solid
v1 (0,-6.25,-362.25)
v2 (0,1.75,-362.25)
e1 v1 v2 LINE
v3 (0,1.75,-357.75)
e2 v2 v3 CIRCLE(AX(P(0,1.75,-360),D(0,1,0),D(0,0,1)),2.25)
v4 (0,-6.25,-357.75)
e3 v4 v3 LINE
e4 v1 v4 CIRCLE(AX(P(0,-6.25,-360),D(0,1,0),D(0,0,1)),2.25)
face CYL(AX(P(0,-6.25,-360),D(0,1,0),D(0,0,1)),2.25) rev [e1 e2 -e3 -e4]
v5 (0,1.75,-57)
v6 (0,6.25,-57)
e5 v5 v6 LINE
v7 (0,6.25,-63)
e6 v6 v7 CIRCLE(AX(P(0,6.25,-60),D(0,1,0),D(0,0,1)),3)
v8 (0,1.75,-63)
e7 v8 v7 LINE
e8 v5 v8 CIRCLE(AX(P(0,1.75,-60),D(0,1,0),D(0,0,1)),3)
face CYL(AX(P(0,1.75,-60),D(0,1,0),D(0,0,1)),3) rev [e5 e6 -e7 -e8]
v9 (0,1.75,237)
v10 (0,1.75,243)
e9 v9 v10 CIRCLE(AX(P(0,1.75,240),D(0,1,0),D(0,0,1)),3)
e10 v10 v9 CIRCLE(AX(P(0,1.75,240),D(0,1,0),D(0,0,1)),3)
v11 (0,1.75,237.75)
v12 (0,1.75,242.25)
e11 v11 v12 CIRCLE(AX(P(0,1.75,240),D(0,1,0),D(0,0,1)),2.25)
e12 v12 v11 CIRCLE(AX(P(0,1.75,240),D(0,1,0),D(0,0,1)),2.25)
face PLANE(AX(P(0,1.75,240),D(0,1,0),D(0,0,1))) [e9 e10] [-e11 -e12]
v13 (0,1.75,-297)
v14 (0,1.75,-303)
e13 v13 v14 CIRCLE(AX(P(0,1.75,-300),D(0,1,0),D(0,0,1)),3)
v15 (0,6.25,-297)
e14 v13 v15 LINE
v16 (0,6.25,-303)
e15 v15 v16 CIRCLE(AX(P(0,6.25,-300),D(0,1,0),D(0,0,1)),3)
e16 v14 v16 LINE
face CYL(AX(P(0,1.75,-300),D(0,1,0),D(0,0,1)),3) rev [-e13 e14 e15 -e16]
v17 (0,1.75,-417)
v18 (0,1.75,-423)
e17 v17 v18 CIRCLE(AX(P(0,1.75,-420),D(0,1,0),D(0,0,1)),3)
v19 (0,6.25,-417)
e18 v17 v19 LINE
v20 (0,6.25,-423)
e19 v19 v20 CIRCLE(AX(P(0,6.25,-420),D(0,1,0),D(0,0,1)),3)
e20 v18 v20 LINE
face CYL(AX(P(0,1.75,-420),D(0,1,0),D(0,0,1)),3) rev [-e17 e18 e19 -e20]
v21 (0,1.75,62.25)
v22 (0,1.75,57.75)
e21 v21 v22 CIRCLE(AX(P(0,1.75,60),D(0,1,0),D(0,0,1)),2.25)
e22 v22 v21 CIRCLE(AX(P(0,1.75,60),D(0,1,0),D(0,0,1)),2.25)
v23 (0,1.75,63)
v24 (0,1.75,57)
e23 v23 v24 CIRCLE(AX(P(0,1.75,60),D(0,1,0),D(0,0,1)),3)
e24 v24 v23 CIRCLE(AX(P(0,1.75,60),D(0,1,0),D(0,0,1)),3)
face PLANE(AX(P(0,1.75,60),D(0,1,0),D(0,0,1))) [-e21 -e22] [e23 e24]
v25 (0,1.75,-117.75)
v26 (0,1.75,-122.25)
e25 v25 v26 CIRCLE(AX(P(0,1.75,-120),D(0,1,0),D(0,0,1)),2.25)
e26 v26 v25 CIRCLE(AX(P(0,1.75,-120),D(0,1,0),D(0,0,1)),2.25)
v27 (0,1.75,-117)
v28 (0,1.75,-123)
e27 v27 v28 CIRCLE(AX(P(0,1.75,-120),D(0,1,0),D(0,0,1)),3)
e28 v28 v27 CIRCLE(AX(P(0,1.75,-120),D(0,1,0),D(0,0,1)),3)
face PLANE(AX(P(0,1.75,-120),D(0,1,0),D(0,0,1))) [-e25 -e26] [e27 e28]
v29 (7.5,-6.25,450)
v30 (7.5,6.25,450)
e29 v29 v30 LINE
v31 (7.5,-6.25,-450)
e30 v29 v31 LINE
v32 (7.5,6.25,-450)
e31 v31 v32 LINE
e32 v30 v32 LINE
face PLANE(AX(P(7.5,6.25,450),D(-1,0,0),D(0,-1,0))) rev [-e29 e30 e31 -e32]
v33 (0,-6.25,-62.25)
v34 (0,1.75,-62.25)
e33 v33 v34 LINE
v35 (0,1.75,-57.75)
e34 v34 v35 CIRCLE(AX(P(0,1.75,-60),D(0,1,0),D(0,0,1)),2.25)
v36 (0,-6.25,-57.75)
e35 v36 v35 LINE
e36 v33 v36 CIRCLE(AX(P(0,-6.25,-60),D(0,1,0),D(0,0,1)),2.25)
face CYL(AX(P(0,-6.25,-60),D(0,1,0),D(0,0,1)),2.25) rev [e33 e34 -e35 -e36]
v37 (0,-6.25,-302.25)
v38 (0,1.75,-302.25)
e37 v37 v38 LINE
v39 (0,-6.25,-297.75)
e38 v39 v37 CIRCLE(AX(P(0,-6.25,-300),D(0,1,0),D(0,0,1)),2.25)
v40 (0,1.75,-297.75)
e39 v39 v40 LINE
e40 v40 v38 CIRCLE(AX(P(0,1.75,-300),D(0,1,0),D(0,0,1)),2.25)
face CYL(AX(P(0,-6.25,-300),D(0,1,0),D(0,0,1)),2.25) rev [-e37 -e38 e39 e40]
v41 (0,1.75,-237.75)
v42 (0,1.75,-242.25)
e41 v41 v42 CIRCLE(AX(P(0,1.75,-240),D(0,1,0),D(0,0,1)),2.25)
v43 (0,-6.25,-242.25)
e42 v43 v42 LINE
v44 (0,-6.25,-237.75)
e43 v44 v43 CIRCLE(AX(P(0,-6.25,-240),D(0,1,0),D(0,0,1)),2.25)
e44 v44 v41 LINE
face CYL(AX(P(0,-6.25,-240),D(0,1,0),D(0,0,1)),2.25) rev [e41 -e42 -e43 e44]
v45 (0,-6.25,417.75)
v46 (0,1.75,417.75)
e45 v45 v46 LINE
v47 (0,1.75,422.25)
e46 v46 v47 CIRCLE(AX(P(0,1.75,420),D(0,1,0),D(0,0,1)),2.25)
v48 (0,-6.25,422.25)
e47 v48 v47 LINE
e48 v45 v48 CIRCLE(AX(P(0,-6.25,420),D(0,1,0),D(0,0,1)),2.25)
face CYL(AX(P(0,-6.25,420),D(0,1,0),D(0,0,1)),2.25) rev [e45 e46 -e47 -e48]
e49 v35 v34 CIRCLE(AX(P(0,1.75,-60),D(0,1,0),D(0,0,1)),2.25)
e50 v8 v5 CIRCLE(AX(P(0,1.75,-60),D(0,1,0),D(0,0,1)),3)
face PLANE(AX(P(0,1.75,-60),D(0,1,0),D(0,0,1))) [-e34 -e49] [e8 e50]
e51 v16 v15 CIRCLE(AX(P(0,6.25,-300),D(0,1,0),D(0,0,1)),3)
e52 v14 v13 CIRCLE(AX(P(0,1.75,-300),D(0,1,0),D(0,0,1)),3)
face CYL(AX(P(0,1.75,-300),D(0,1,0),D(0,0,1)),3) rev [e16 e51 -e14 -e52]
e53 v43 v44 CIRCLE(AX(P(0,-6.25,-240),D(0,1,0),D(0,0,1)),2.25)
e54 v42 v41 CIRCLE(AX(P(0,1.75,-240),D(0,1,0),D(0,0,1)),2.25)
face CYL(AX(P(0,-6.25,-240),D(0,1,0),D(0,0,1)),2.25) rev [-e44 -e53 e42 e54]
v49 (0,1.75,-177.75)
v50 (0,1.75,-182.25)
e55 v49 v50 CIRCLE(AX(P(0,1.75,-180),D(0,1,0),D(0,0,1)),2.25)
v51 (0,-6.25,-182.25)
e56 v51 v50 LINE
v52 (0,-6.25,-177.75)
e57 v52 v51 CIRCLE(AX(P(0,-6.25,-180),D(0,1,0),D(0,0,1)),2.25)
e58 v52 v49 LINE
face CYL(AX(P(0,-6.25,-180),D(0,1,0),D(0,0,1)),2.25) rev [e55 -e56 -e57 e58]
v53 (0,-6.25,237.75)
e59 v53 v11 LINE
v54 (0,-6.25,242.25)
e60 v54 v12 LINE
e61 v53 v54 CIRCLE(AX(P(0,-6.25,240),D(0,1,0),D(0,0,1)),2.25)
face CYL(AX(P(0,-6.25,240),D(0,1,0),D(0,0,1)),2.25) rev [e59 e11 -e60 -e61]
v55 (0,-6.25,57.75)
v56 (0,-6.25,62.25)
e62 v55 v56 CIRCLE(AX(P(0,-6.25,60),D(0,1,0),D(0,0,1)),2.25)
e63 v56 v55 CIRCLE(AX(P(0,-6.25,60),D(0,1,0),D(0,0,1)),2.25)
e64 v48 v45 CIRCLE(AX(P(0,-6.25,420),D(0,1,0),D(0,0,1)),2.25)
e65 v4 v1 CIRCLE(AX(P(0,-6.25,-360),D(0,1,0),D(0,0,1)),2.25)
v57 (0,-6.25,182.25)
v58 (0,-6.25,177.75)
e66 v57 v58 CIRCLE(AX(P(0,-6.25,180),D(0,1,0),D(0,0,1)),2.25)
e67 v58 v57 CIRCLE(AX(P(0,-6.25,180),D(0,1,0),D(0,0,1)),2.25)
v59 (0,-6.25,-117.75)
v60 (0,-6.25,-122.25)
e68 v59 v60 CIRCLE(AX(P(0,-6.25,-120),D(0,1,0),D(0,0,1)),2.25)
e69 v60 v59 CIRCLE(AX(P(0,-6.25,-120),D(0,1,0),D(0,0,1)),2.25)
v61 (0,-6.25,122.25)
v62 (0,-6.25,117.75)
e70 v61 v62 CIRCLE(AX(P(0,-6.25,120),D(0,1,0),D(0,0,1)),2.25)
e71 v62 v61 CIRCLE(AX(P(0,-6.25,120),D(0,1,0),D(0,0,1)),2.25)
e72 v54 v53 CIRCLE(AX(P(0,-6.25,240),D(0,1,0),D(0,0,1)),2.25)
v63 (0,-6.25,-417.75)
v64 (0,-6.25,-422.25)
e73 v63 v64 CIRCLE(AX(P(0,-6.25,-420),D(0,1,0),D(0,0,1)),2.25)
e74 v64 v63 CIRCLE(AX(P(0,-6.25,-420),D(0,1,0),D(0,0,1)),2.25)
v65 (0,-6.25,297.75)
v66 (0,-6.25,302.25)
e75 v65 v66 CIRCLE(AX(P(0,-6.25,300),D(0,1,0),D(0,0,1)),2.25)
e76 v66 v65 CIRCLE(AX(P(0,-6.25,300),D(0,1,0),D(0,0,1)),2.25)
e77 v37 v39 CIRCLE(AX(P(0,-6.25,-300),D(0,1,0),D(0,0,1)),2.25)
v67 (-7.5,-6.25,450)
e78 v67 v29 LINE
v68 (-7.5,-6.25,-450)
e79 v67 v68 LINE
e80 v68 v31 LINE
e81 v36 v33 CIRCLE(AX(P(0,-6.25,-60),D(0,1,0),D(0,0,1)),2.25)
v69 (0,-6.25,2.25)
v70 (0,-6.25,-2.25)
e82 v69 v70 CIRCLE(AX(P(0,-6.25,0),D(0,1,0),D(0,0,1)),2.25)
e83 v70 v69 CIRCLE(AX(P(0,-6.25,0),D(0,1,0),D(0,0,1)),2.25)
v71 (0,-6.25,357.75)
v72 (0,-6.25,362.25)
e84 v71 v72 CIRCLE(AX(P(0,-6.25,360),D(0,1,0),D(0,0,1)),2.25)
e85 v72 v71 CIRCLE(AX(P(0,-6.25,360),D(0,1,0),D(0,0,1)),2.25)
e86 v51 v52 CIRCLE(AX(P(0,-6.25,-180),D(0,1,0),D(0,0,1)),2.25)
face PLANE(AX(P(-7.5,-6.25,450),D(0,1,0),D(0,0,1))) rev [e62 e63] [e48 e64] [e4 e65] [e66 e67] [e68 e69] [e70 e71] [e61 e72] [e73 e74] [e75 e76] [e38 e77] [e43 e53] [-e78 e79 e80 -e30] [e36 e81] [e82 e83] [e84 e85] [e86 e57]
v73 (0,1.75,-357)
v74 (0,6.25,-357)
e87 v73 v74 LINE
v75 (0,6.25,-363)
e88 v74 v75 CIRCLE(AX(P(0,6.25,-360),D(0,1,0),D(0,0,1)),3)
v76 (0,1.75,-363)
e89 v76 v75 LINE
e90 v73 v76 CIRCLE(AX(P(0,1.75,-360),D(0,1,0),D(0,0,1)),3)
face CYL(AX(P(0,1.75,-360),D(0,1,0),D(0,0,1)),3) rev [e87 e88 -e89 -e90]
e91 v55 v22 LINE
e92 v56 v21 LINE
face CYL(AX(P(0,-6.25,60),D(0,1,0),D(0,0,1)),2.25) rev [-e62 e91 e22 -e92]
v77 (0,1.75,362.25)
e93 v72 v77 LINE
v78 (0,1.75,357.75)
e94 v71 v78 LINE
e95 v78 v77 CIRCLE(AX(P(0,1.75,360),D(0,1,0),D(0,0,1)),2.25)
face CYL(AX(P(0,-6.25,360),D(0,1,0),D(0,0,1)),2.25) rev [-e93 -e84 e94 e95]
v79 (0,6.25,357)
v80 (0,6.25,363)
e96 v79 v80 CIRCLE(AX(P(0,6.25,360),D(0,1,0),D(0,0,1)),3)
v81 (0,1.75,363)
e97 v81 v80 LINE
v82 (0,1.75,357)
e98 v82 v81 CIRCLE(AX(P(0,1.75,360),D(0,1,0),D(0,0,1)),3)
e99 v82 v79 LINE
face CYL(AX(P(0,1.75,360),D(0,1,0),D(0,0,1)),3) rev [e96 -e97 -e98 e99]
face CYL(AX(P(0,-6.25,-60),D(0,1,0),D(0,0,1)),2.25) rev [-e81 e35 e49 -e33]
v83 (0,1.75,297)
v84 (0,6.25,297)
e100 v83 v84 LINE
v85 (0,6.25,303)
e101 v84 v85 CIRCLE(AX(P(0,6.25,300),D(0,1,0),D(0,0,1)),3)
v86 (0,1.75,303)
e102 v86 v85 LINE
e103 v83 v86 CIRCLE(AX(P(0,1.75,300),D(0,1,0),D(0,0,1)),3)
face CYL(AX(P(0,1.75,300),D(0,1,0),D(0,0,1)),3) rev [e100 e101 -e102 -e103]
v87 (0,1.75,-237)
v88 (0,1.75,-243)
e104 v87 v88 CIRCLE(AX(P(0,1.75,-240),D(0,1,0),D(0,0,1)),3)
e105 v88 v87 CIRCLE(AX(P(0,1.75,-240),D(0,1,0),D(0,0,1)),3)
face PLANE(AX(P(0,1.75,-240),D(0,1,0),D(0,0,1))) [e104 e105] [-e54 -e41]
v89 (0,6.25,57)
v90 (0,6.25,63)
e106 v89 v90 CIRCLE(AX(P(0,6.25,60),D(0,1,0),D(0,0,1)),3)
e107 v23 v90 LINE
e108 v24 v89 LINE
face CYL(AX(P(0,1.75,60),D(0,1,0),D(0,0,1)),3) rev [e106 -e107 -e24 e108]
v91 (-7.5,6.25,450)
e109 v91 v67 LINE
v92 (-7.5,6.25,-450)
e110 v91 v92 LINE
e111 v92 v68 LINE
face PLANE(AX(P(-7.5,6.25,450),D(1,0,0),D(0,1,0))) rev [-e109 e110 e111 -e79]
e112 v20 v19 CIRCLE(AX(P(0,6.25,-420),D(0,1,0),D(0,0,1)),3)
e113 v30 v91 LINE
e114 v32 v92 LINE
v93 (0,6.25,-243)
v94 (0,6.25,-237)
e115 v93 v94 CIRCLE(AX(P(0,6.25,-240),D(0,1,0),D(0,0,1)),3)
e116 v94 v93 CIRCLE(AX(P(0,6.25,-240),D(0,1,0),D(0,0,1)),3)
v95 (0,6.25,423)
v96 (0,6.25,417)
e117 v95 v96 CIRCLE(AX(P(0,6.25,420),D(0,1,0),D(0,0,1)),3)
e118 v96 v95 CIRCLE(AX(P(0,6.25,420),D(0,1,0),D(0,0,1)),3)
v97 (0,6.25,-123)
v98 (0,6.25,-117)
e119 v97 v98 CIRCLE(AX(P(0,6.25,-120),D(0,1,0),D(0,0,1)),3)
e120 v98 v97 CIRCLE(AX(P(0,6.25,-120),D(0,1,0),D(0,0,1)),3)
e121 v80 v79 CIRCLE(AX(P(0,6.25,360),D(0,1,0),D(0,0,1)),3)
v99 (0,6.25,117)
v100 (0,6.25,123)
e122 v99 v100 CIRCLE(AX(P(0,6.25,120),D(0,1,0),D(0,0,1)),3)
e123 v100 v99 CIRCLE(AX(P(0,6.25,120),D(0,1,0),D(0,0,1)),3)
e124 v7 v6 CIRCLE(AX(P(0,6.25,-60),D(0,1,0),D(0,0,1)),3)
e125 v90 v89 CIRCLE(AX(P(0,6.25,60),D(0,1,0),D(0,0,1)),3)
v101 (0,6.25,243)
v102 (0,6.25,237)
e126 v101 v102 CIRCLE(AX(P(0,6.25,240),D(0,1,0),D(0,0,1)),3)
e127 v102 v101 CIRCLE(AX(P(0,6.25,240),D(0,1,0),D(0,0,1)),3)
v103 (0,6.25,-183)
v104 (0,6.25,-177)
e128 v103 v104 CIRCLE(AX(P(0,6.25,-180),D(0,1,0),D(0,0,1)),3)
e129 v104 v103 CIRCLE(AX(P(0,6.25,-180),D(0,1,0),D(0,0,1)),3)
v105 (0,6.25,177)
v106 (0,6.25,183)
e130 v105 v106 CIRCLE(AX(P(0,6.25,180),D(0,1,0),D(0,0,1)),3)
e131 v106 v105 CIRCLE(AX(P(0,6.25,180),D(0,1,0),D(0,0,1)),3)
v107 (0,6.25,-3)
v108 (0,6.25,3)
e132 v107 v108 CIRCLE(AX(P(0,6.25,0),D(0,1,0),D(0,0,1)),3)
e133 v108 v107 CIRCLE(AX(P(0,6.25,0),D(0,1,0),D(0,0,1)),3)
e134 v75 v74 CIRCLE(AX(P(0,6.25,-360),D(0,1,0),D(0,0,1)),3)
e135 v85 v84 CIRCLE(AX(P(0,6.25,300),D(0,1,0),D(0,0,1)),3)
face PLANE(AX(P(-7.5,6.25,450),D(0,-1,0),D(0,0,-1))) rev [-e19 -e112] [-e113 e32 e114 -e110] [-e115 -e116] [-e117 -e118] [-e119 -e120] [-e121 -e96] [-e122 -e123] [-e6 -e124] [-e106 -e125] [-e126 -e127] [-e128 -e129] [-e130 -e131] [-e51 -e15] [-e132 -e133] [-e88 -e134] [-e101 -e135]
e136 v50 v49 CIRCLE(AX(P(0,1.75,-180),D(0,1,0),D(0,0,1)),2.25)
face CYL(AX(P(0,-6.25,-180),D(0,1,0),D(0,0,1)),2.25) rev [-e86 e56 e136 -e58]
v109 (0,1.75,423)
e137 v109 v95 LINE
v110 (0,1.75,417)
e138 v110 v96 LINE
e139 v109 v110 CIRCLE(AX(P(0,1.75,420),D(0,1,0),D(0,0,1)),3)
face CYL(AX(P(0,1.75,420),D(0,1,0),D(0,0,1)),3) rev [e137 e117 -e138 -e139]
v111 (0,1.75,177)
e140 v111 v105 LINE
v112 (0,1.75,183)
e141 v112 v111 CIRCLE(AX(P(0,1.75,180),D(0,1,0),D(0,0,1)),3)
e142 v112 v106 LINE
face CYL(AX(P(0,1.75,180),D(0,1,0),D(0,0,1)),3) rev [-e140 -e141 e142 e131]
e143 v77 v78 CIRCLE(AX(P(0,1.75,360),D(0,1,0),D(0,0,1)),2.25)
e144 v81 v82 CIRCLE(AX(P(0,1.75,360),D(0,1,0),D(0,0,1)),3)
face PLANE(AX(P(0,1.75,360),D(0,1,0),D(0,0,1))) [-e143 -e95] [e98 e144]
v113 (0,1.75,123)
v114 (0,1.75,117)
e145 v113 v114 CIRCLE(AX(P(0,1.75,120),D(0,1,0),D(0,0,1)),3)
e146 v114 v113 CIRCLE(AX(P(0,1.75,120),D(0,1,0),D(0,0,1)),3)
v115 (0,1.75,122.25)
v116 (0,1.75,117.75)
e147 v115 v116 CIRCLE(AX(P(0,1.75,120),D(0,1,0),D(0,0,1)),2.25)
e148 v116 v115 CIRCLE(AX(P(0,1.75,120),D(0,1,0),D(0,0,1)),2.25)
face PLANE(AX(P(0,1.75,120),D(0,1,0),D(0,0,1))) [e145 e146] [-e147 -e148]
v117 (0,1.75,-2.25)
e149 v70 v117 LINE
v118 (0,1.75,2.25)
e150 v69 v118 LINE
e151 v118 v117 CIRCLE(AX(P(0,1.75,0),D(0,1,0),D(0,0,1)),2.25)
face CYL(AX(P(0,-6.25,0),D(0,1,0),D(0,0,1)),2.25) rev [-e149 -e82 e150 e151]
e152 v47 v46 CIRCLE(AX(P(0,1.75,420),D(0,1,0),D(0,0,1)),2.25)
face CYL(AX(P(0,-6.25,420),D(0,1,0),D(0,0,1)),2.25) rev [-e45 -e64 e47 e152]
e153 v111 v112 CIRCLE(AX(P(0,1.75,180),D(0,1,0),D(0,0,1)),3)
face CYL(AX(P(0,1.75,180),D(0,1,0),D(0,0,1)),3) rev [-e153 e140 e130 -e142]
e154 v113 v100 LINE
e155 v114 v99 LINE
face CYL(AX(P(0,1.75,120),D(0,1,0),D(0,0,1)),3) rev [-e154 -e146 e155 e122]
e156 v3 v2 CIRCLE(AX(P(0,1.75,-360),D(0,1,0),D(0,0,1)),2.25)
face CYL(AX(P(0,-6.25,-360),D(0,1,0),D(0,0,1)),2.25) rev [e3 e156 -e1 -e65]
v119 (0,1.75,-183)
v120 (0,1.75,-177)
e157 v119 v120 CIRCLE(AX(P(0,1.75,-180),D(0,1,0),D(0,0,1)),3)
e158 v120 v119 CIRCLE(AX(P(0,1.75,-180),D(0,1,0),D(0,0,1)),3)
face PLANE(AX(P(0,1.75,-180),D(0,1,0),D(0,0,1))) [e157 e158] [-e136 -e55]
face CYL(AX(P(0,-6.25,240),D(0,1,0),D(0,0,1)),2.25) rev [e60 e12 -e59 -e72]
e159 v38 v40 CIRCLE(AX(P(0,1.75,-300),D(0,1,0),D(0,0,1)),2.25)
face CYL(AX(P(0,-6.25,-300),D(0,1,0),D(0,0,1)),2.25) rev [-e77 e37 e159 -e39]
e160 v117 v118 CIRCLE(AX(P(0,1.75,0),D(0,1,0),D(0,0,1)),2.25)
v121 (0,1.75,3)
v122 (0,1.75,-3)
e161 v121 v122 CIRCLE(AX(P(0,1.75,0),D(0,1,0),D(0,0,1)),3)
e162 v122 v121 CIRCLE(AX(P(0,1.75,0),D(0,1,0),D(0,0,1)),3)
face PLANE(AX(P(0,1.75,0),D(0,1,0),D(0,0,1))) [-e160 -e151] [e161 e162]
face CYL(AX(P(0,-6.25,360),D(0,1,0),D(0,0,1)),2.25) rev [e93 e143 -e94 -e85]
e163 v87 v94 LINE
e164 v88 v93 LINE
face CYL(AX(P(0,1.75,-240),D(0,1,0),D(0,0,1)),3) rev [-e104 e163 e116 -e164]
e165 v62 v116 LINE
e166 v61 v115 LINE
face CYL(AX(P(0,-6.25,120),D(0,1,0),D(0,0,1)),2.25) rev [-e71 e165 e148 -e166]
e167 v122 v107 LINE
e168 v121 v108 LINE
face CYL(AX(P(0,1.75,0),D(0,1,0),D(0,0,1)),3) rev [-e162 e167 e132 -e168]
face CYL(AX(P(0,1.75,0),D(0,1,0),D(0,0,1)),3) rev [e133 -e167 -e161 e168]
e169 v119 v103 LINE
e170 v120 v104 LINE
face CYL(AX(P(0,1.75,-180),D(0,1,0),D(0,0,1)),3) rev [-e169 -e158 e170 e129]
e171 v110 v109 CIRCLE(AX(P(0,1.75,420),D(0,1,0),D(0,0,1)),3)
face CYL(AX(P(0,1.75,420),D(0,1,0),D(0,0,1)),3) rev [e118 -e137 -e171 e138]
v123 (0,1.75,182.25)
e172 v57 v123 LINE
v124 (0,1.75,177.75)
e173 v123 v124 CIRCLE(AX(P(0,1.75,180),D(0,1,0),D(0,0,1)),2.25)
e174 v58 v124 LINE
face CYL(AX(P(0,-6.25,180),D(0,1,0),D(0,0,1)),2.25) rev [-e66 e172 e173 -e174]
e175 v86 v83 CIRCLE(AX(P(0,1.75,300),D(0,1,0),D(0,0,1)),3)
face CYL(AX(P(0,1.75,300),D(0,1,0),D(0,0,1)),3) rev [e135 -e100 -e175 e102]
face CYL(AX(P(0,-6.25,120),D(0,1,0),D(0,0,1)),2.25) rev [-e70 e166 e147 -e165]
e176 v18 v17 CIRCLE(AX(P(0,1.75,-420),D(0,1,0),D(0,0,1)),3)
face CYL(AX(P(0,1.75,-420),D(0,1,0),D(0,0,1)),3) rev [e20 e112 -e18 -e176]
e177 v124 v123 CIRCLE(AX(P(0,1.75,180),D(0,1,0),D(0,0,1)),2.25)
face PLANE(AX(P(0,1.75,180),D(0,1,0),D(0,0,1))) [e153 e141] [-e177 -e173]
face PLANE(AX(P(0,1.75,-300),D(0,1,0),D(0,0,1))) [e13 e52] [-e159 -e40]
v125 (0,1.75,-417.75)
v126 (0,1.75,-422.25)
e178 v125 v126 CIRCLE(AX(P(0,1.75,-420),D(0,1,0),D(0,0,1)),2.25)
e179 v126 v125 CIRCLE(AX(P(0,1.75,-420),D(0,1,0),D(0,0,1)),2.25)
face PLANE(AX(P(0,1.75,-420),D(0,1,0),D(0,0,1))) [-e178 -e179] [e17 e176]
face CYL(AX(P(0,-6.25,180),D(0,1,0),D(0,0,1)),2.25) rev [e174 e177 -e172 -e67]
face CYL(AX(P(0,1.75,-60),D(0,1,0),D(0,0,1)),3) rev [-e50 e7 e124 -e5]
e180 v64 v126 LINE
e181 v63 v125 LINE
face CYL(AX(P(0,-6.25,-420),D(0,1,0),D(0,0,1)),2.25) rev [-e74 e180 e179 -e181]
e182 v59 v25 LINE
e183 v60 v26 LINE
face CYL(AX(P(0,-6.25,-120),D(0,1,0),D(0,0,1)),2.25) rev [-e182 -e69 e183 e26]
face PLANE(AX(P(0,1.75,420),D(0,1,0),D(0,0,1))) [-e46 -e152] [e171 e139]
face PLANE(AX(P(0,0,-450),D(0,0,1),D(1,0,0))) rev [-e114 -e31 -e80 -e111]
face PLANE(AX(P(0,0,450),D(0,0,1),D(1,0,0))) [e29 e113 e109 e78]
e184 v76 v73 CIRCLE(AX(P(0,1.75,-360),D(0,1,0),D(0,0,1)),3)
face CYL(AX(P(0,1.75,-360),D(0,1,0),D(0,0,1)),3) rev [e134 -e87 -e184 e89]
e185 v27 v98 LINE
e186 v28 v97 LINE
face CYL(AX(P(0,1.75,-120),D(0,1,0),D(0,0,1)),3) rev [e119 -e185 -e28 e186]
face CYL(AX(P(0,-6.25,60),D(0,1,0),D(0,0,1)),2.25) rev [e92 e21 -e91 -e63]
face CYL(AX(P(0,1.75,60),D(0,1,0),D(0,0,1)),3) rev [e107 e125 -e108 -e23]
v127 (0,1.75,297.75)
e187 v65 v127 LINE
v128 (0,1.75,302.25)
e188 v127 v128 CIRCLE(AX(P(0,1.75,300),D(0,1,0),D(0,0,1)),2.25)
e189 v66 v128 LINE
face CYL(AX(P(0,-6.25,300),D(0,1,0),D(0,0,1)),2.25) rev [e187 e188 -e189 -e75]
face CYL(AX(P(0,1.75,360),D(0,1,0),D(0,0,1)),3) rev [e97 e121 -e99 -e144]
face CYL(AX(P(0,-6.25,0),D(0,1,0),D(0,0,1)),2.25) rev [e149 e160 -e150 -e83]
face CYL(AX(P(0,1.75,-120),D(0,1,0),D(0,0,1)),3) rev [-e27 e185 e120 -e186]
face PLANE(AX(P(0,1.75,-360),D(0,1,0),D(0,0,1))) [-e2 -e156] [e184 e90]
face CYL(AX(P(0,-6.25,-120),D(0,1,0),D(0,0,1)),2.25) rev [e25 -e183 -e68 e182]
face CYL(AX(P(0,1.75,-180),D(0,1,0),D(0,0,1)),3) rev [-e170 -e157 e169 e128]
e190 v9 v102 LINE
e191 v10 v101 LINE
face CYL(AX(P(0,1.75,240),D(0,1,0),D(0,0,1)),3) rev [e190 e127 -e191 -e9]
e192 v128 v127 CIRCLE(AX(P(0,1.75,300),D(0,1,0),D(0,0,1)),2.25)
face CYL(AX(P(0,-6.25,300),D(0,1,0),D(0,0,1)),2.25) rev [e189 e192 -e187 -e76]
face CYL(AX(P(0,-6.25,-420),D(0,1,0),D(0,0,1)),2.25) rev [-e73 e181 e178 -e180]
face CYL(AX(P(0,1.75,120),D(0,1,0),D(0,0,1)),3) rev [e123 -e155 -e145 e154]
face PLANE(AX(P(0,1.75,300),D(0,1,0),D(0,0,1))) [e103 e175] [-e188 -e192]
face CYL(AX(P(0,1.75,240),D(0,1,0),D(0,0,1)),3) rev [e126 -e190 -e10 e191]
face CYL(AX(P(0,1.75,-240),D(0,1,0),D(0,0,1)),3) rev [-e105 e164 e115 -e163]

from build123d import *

# Parameters (mm, degrees)
SKETCH_1_W             = 15
SKETCH_1_H             = 12.5
EXTRUDE_1_DEPTH        = 450
SKETCH_2_R             = 3
CUT_EXTRUDE_1_DEPTH    = 4.5
SKETCH_3_R             = 2.25
CUT_EXTRUDE_2_DEPTH    = 451.236049201
PATTERN_LINEAR_1_COUNT = 16
PATTERN_LINEAR_1_PITCH = 60


with BuildPart() as part:
    # 草图1 → 凸台-拉伸1 (new, symmetric)
    with BuildSketch(Plane.XY):
        Rectangle(SKETCH_1_W, SKETCH_1_H)
    extrude(amount=EXTRUDE_1_DEPTH, both=True)

    # 草图2 → 切除-拉伸1 (cut)
    with BuildSketch(Plane(origin=(0, 6.25, 0), x_dir=(1, 0, 0), z_dir=(0, 1, 0))):
        with Locations(Location((0, -420, 0), (0, 0, 270))):
            Circle(SKETCH_2_R)
    cut_extrude_1 = extrude(amount=-CUT_EXTRUDE_1_DEPTH, mode=Mode.SUBTRACT)

    # 草图3 → 切除-拉伸2 (cut, through all)
    with BuildSketch(Plane(origin=(0, 6.25, 0), x_dir=(1, 0, 0), z_dir=(0, 1, 0))):
        with Locations(Location((0, -420, 0), (0, 0, 270))):
            Circle(SKETCH_3_R)
    cut_extrude_2 = extrude(amount=-CUT_EXTRUDE_2_DEPTH, mode=Mode.SUBTRACT)

    # 阵列(线性)1: 切除-拉伸1, 切除-拉伸2 ×16
    with Locations(*[(0, 0, -i * PATTERN_LINEAR_1_PITCH) for i in range(1, PATTERN_LINEAR_1_COUNT)]):
        add(cut_extrude_1, mode=Mode.SUBTRACT)
        add(cut_extrude_2, mode=Mode.SUBTRACT)


solid = part.part
